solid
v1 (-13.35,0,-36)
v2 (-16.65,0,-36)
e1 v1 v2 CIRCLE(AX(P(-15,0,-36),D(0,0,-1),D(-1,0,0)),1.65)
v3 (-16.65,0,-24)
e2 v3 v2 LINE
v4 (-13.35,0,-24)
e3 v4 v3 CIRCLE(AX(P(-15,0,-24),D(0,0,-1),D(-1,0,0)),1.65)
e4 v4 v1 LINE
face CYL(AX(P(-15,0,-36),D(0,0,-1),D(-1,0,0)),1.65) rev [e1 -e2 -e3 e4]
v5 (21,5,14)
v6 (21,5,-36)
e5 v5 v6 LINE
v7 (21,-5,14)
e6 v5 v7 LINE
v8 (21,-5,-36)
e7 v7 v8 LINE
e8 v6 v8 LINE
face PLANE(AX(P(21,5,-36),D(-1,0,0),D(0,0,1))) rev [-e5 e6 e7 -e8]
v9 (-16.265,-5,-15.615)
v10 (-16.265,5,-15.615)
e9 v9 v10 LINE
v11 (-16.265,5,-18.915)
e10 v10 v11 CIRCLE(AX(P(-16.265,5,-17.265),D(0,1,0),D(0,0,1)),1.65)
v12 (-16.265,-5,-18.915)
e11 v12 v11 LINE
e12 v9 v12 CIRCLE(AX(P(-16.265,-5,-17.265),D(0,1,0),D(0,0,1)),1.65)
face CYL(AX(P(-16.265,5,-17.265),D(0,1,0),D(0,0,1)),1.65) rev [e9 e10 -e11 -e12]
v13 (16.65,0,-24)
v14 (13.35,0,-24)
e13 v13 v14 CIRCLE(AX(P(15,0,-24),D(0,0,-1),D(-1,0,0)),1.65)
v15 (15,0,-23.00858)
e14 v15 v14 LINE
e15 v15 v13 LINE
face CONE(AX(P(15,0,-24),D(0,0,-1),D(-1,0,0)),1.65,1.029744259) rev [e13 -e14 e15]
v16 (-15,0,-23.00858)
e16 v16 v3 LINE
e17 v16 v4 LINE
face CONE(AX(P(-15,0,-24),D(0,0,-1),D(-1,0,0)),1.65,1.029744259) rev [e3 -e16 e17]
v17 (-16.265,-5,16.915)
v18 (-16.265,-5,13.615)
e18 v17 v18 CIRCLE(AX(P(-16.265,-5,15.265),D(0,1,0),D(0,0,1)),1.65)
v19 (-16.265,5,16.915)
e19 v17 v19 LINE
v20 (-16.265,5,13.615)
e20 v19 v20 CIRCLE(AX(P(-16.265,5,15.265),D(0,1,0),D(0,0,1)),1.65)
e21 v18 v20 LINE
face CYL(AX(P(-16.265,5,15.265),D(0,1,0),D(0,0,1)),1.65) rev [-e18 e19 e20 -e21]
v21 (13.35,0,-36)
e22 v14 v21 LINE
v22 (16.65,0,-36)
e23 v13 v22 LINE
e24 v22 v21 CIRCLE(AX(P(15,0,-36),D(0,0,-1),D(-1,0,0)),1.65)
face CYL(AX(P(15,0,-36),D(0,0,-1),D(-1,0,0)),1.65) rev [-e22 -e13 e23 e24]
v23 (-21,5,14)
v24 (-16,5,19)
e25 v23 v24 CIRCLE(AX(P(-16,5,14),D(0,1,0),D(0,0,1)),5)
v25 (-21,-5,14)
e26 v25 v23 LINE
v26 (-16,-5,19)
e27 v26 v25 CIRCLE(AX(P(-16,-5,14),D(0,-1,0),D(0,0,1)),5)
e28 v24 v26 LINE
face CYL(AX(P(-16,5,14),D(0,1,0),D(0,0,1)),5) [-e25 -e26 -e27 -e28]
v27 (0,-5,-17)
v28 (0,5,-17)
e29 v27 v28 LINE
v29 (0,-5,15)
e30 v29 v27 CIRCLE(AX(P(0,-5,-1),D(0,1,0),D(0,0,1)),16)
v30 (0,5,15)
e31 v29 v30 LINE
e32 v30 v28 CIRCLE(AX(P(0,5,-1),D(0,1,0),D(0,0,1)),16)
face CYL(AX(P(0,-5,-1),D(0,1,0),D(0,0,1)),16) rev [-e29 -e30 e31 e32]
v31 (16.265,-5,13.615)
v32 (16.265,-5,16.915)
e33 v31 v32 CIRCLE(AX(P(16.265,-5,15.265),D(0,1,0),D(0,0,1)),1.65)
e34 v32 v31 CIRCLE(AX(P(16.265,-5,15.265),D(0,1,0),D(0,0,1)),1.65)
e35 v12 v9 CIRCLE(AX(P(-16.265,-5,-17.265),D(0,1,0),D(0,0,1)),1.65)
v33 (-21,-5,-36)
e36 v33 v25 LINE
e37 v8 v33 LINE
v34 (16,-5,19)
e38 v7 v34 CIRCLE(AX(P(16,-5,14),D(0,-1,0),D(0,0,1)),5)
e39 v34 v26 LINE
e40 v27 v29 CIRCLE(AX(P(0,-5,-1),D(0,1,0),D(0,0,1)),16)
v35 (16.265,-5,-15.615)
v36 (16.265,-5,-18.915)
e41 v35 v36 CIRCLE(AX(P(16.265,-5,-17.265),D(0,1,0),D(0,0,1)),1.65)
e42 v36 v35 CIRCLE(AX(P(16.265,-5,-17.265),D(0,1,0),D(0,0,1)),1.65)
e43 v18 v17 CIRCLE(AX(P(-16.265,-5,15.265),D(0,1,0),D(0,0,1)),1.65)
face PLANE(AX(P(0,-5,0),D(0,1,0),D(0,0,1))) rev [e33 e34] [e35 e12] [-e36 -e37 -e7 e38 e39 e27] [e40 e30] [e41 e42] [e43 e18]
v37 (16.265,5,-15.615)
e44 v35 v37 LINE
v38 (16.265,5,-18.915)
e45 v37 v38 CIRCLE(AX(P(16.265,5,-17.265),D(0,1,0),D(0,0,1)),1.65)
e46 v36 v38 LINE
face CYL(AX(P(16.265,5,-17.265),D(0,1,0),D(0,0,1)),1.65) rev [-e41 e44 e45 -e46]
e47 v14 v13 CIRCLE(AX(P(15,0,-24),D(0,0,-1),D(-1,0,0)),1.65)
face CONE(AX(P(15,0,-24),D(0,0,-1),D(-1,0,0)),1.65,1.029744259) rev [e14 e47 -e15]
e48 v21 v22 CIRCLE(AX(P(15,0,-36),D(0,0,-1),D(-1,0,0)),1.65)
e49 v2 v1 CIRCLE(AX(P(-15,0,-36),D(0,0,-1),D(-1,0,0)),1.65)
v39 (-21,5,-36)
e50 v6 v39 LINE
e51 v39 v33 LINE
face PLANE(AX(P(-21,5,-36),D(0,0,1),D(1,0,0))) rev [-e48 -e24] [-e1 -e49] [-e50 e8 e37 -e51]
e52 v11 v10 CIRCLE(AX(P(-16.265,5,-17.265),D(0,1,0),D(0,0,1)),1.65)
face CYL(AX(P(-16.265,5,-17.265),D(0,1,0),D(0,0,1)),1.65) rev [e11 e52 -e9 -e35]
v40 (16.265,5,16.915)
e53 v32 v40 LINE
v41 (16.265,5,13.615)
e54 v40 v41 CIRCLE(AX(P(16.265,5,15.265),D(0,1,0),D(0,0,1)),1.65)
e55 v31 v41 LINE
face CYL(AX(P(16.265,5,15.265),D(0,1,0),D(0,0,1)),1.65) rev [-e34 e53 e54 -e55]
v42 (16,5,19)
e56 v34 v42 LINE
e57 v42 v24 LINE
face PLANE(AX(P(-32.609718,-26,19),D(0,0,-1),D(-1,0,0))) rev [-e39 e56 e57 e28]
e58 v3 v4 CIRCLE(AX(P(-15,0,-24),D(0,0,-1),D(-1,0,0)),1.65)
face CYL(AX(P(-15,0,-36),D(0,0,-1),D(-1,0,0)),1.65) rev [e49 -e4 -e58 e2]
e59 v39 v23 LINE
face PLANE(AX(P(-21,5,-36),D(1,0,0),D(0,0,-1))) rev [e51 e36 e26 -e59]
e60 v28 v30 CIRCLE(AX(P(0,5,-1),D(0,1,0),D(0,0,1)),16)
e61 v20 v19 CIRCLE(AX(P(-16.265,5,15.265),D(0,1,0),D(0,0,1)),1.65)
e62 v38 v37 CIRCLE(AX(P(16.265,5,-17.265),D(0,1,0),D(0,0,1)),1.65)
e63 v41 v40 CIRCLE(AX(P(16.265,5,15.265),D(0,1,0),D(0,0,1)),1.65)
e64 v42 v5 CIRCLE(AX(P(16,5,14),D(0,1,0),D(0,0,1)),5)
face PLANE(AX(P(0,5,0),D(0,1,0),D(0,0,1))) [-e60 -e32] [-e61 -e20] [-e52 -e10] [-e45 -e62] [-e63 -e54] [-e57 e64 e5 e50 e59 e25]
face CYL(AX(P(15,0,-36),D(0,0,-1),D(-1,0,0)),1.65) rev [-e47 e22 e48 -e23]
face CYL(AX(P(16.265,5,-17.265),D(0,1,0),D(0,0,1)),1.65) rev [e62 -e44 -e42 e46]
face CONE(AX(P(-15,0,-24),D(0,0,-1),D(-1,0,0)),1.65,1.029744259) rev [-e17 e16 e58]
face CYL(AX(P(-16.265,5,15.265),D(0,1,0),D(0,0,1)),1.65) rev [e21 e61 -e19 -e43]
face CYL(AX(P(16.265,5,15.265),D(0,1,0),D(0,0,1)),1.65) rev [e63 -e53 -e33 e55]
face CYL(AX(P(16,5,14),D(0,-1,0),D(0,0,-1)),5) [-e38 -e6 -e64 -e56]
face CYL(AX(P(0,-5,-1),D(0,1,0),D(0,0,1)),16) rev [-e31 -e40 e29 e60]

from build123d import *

# Parameters (mm, degrees)
SKETCH_1_W             = 42
SKETCH_1_H             = 72
EXTRUDE_1_DEPTH        = 5
HOLE_WIZARD_M4_2_D     = 3.3
HOLE_WIZARD_M4_2_DEPTH = 12
HOLE_WIZARD_M4_2_TIP   = 0.991420021
SKETCH_6_R             = 16
CUT_EXTRUDE_1_DEPTH    = 43.860237983
CHAMFER_2_SIZE         = 10
FILLET_1_R             = 5
SKETCH_15_W            = 77.686914385
SKETCH_15_H            = 52.90814048
CUT_EXTRUDE_3_DEPTH    = 31
FILLET_2_R             = 5
HOLE_WIZARD_M4_1_D     = 3.3


with BuildPart() as part:
    # 草图1 → 凸台-拉伸1 (new, symmetric)
    with BuildSketch(Plane(origin=(0, 0, 0), x_dir=(1, 0, 0), z_dir=(0, 1, 0))):
        Rectangle(SKETCH_1_W, SKETCH_1_H)
    extrude(amount=EXTRUDE_1_DEPTH, both=True)

    # M4 螺纹孔2
    with Locations(Plane(origin=(0, 0, -36), x_dir=(-1, 0, 0), z_dir=(0, 0, -1))):
        with Locations((-15, 0), (15, 0)):
            Hole(HOLE_WIZARD_M4_2_D / 2, depth=HOLE_WIZARD_M4_2_DEPTH)
            with Locations((0, 0, -(HOLE_WIZARD_M4_2_DEPTH + HOLE_WIZARD_M4_2_TIP / 2))):  # 118° drill point
                Cone(0, HOLE_WIZARD_M4_2_D / 2, HOLE_WIZARD_M4_2_TIP, mode=Mode.SUBTRACT)

    # 草图6 → 切除-拉伸1 (cut, through all)
    with BuildSketch(Plane(origin=(0, 5, 0), x_dir=(1, 0, 0), z_dir=(0, 1, 0))):
        with Locations(Location((0, 1, 0), (0, 0, 270))):
            Circle(SKETCH_6_R)
    extrude(amount=-CUT_EXTRUDE_1_DEPTH, mode=Mode.SUBTRACT)

    # 倒角2
    chamfer_2_edges = [part.edges().sort_by_distance(p)[0] for p in [
        (21, 0, 36),
        (-21, 0, 36),
    ]]
    chamfer(chamfer_2_edges, length=CHAMFER_2_SIZE)

    # 圆角1
    fillet_1_edges = [part.edges().sort_by_distance(p)[0] for p in [
        (11, 0, 36),
        (-11, 0, 36),
        (-21, 0, 26),
        (21, 0, 26),
    ]]
    fillet(fillet_1_edges, radius=FILLET_1_R)

    # 草图15 → 切除-拉伸3 (cut)
    with BuildSketch(Plane(origin=(0, 5, 0), x_dir=(1, 0, 0), z_dir=(0, 1, 0))):
        with Locations((6.233739535, -45.45407024)):
            Rectangle(SKETCH_15_W, SKETCH_15_H)
    extrude(amount=-CUT_EXTRUDE_3_DEPTH, mode=Mode.SUBTRACT)

    # 圆角2
    fillet_2_edges = [part.edges().sort_by_distance(p)[0] for p in [
        (21, 0, 19),
        (-21, 0, 19),
    ]]
    fillet(fillet_2_edges, radius=FILLET_2_R)

    # M4 螺纹孔1 (through all)
    with Locations(Plane(origin=(0, 5, 0), x_dir=(1, 0, 0), z_dir=(0, 1, 0))):
        with Locations((-16.265, 17.265), (16.265, 17.265), (-16.265, -15.265), (16.265, -15.265)):
            Hole(HOLE_WIZARD_M4_1_D / 2)


solid = part.part
